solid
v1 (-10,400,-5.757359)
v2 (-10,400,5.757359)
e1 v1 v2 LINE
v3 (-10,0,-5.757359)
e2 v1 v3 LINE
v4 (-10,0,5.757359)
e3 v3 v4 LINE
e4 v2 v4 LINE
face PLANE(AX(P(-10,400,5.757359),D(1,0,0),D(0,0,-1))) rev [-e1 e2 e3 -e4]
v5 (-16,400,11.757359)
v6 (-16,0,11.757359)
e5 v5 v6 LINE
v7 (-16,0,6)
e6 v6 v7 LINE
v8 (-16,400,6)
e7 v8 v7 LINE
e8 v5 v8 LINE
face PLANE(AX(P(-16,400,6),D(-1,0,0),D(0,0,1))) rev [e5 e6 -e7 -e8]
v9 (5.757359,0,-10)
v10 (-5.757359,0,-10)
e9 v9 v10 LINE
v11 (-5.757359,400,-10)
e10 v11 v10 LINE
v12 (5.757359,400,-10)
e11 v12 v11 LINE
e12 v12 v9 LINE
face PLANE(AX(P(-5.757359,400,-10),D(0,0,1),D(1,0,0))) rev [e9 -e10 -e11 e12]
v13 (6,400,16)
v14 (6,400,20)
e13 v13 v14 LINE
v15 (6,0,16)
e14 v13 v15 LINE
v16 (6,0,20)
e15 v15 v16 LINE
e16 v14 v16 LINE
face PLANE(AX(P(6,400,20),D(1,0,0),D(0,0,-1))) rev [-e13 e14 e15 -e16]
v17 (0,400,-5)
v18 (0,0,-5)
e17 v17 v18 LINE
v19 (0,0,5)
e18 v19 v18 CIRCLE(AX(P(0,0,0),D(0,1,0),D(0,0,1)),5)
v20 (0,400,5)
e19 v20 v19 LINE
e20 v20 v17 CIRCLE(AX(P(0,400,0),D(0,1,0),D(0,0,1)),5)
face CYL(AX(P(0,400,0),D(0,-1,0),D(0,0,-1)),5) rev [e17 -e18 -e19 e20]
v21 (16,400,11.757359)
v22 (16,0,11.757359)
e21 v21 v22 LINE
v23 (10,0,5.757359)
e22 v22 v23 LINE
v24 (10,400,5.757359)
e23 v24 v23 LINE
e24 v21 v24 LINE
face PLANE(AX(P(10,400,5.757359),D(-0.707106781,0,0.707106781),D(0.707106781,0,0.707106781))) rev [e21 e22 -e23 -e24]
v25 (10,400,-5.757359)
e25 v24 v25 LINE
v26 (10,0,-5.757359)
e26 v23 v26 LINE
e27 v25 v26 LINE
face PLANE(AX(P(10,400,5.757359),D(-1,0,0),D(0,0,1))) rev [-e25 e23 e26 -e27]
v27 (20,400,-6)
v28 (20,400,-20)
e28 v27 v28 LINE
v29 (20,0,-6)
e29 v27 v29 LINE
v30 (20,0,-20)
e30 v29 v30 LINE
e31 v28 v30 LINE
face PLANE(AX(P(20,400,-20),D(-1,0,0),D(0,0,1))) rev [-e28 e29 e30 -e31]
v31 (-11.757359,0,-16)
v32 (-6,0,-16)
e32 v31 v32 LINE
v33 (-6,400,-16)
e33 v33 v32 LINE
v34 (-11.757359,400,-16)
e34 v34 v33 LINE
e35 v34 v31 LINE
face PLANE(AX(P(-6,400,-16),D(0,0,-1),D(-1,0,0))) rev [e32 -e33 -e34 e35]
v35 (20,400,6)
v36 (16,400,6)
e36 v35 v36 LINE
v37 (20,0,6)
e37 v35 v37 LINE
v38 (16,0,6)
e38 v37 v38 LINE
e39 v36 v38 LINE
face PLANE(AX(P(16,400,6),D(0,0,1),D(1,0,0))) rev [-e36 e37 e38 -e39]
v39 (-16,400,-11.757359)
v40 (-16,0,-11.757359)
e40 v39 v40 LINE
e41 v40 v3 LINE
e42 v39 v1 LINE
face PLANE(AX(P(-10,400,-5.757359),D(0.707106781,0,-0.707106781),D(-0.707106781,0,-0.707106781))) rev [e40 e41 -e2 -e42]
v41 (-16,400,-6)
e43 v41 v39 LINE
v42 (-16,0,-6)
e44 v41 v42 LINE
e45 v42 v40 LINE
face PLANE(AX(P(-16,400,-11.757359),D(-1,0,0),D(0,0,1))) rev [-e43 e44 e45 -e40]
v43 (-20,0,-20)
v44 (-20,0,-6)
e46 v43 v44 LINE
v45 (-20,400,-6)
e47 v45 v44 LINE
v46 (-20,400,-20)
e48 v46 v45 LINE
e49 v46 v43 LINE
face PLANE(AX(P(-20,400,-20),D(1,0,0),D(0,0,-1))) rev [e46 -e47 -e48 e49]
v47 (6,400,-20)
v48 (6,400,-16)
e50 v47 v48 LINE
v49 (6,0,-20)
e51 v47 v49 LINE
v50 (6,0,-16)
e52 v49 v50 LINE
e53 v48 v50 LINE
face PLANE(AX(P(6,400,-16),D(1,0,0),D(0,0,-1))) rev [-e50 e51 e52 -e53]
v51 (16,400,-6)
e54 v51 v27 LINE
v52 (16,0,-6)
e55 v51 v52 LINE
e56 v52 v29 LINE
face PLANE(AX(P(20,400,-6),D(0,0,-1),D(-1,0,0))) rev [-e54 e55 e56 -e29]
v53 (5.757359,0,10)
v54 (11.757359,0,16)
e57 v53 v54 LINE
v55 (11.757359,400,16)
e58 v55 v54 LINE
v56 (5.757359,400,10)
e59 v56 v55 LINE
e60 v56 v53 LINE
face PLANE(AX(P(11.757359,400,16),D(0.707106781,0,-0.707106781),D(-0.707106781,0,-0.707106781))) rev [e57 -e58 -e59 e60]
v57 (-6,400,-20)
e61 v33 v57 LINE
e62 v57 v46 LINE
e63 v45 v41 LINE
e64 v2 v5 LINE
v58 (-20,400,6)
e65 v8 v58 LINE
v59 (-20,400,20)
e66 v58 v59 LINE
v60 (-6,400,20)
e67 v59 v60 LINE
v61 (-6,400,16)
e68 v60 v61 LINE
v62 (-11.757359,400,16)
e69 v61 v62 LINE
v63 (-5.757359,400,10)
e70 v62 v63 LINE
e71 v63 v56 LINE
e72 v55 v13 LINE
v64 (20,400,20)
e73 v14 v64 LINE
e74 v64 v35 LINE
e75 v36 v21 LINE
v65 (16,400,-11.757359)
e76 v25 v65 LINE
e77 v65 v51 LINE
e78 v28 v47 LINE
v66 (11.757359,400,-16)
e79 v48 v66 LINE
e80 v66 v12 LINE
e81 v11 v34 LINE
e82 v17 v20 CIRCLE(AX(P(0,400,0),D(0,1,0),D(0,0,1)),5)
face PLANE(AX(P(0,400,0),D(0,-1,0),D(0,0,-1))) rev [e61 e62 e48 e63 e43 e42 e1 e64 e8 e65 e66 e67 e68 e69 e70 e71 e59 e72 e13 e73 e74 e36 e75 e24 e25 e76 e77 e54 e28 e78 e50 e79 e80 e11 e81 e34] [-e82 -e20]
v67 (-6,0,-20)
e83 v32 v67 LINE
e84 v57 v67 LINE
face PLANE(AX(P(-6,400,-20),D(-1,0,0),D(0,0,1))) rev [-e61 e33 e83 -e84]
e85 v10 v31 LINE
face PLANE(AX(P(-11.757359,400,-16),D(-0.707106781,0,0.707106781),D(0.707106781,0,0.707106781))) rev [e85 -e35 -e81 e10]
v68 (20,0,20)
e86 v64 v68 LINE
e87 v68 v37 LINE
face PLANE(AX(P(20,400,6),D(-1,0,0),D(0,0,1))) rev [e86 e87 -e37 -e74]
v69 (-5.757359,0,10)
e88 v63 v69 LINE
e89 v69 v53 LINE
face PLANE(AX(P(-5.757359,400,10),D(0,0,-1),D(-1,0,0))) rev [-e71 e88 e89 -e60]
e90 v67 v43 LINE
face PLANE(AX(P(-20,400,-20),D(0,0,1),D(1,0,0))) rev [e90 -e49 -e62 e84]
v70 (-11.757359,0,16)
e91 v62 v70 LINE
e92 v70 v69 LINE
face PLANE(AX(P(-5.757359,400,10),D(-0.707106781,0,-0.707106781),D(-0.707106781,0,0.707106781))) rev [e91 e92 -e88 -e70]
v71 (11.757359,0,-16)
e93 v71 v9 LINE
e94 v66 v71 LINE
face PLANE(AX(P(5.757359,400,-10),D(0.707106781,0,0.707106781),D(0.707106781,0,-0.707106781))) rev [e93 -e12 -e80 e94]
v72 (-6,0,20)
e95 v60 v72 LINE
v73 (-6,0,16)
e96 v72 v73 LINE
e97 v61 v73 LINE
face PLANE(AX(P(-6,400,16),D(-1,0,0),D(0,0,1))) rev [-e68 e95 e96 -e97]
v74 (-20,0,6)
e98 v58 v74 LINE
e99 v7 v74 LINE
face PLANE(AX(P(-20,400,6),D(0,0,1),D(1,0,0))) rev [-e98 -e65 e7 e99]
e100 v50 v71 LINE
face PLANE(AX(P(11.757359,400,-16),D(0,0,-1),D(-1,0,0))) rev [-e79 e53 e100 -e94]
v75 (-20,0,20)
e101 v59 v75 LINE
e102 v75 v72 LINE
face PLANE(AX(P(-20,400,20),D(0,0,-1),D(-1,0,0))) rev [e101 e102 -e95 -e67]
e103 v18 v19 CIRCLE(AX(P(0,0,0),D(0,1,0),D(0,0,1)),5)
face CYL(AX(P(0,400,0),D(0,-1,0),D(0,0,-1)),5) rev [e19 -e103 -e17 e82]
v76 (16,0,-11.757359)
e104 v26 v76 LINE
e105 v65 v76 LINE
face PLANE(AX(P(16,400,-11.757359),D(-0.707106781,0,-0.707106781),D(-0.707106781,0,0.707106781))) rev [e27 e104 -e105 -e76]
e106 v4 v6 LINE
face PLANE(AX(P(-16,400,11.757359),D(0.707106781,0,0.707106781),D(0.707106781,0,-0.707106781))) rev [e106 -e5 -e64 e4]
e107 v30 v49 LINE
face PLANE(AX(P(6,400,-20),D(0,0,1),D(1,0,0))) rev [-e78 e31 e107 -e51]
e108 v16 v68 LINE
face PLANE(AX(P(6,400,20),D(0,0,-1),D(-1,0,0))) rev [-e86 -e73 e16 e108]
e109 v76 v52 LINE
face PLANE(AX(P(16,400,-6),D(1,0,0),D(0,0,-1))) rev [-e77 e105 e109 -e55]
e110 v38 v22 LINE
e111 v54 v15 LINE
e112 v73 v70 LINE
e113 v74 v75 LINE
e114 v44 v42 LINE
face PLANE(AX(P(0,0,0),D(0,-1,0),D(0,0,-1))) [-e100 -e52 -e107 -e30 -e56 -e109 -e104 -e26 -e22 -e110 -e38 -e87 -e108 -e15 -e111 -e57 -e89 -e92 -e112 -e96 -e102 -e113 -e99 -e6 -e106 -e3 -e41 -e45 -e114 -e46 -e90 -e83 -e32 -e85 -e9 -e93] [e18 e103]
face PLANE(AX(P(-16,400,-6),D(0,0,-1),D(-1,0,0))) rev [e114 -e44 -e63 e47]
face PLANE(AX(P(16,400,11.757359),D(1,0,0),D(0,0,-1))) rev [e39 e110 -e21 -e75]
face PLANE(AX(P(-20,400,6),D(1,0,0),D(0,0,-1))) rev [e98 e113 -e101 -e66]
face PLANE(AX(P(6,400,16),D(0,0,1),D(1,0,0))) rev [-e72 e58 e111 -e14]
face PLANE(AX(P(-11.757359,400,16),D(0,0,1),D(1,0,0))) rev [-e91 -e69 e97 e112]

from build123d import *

# Parameters (mm, degrees)
SKETCH1_R           = 5
BOSS_EXTRUDE1_DEPTH = 400


with BuildPart() as part:
    # Sketch1 → Boss-Extrude1 (new body)
    with BuildSketch(Plane(origin=(0, 0, 0), x_dir=(1, 0, 0), z_dir=(0, 1, 0))):
        Polygon((-6, 20), (-6, 16), (-11.757359313, 16), (-5.757359313, 10), (5.757359313, 10), (11.757359313, 16), (6, 16), (6, 20), (20, 20), (20, 6), (16, 6), (16, 11.757359313), (10, 5.757359313), (10, -5.757359313), (16, -11.757359313), (16, -6), (20, -6), (20, -20), (6, -20), (6, -16), (11.757359313, -16), (5.757359313, -10), (-5.757359313, -10), (-11.757359313, -16), (-6, -16), (-6, -20), (-20, -20), (-20, -6), (-16, -6), (-16, -11.757359313), (-10, -5.757359313), (-10, 5.757359313), (-16, 11.757359313), (-16, 6), (-20, 6), (-20, 20), align=None)
        with Locations(Location((0, 0, 0), (0, 0, 270))):
            Circle(SKETCH1_R, mode=Mode.SUBTRACT)
    extrude(amount=BOSS_EXTRUDE1_DEPTH)


solid = part.part
